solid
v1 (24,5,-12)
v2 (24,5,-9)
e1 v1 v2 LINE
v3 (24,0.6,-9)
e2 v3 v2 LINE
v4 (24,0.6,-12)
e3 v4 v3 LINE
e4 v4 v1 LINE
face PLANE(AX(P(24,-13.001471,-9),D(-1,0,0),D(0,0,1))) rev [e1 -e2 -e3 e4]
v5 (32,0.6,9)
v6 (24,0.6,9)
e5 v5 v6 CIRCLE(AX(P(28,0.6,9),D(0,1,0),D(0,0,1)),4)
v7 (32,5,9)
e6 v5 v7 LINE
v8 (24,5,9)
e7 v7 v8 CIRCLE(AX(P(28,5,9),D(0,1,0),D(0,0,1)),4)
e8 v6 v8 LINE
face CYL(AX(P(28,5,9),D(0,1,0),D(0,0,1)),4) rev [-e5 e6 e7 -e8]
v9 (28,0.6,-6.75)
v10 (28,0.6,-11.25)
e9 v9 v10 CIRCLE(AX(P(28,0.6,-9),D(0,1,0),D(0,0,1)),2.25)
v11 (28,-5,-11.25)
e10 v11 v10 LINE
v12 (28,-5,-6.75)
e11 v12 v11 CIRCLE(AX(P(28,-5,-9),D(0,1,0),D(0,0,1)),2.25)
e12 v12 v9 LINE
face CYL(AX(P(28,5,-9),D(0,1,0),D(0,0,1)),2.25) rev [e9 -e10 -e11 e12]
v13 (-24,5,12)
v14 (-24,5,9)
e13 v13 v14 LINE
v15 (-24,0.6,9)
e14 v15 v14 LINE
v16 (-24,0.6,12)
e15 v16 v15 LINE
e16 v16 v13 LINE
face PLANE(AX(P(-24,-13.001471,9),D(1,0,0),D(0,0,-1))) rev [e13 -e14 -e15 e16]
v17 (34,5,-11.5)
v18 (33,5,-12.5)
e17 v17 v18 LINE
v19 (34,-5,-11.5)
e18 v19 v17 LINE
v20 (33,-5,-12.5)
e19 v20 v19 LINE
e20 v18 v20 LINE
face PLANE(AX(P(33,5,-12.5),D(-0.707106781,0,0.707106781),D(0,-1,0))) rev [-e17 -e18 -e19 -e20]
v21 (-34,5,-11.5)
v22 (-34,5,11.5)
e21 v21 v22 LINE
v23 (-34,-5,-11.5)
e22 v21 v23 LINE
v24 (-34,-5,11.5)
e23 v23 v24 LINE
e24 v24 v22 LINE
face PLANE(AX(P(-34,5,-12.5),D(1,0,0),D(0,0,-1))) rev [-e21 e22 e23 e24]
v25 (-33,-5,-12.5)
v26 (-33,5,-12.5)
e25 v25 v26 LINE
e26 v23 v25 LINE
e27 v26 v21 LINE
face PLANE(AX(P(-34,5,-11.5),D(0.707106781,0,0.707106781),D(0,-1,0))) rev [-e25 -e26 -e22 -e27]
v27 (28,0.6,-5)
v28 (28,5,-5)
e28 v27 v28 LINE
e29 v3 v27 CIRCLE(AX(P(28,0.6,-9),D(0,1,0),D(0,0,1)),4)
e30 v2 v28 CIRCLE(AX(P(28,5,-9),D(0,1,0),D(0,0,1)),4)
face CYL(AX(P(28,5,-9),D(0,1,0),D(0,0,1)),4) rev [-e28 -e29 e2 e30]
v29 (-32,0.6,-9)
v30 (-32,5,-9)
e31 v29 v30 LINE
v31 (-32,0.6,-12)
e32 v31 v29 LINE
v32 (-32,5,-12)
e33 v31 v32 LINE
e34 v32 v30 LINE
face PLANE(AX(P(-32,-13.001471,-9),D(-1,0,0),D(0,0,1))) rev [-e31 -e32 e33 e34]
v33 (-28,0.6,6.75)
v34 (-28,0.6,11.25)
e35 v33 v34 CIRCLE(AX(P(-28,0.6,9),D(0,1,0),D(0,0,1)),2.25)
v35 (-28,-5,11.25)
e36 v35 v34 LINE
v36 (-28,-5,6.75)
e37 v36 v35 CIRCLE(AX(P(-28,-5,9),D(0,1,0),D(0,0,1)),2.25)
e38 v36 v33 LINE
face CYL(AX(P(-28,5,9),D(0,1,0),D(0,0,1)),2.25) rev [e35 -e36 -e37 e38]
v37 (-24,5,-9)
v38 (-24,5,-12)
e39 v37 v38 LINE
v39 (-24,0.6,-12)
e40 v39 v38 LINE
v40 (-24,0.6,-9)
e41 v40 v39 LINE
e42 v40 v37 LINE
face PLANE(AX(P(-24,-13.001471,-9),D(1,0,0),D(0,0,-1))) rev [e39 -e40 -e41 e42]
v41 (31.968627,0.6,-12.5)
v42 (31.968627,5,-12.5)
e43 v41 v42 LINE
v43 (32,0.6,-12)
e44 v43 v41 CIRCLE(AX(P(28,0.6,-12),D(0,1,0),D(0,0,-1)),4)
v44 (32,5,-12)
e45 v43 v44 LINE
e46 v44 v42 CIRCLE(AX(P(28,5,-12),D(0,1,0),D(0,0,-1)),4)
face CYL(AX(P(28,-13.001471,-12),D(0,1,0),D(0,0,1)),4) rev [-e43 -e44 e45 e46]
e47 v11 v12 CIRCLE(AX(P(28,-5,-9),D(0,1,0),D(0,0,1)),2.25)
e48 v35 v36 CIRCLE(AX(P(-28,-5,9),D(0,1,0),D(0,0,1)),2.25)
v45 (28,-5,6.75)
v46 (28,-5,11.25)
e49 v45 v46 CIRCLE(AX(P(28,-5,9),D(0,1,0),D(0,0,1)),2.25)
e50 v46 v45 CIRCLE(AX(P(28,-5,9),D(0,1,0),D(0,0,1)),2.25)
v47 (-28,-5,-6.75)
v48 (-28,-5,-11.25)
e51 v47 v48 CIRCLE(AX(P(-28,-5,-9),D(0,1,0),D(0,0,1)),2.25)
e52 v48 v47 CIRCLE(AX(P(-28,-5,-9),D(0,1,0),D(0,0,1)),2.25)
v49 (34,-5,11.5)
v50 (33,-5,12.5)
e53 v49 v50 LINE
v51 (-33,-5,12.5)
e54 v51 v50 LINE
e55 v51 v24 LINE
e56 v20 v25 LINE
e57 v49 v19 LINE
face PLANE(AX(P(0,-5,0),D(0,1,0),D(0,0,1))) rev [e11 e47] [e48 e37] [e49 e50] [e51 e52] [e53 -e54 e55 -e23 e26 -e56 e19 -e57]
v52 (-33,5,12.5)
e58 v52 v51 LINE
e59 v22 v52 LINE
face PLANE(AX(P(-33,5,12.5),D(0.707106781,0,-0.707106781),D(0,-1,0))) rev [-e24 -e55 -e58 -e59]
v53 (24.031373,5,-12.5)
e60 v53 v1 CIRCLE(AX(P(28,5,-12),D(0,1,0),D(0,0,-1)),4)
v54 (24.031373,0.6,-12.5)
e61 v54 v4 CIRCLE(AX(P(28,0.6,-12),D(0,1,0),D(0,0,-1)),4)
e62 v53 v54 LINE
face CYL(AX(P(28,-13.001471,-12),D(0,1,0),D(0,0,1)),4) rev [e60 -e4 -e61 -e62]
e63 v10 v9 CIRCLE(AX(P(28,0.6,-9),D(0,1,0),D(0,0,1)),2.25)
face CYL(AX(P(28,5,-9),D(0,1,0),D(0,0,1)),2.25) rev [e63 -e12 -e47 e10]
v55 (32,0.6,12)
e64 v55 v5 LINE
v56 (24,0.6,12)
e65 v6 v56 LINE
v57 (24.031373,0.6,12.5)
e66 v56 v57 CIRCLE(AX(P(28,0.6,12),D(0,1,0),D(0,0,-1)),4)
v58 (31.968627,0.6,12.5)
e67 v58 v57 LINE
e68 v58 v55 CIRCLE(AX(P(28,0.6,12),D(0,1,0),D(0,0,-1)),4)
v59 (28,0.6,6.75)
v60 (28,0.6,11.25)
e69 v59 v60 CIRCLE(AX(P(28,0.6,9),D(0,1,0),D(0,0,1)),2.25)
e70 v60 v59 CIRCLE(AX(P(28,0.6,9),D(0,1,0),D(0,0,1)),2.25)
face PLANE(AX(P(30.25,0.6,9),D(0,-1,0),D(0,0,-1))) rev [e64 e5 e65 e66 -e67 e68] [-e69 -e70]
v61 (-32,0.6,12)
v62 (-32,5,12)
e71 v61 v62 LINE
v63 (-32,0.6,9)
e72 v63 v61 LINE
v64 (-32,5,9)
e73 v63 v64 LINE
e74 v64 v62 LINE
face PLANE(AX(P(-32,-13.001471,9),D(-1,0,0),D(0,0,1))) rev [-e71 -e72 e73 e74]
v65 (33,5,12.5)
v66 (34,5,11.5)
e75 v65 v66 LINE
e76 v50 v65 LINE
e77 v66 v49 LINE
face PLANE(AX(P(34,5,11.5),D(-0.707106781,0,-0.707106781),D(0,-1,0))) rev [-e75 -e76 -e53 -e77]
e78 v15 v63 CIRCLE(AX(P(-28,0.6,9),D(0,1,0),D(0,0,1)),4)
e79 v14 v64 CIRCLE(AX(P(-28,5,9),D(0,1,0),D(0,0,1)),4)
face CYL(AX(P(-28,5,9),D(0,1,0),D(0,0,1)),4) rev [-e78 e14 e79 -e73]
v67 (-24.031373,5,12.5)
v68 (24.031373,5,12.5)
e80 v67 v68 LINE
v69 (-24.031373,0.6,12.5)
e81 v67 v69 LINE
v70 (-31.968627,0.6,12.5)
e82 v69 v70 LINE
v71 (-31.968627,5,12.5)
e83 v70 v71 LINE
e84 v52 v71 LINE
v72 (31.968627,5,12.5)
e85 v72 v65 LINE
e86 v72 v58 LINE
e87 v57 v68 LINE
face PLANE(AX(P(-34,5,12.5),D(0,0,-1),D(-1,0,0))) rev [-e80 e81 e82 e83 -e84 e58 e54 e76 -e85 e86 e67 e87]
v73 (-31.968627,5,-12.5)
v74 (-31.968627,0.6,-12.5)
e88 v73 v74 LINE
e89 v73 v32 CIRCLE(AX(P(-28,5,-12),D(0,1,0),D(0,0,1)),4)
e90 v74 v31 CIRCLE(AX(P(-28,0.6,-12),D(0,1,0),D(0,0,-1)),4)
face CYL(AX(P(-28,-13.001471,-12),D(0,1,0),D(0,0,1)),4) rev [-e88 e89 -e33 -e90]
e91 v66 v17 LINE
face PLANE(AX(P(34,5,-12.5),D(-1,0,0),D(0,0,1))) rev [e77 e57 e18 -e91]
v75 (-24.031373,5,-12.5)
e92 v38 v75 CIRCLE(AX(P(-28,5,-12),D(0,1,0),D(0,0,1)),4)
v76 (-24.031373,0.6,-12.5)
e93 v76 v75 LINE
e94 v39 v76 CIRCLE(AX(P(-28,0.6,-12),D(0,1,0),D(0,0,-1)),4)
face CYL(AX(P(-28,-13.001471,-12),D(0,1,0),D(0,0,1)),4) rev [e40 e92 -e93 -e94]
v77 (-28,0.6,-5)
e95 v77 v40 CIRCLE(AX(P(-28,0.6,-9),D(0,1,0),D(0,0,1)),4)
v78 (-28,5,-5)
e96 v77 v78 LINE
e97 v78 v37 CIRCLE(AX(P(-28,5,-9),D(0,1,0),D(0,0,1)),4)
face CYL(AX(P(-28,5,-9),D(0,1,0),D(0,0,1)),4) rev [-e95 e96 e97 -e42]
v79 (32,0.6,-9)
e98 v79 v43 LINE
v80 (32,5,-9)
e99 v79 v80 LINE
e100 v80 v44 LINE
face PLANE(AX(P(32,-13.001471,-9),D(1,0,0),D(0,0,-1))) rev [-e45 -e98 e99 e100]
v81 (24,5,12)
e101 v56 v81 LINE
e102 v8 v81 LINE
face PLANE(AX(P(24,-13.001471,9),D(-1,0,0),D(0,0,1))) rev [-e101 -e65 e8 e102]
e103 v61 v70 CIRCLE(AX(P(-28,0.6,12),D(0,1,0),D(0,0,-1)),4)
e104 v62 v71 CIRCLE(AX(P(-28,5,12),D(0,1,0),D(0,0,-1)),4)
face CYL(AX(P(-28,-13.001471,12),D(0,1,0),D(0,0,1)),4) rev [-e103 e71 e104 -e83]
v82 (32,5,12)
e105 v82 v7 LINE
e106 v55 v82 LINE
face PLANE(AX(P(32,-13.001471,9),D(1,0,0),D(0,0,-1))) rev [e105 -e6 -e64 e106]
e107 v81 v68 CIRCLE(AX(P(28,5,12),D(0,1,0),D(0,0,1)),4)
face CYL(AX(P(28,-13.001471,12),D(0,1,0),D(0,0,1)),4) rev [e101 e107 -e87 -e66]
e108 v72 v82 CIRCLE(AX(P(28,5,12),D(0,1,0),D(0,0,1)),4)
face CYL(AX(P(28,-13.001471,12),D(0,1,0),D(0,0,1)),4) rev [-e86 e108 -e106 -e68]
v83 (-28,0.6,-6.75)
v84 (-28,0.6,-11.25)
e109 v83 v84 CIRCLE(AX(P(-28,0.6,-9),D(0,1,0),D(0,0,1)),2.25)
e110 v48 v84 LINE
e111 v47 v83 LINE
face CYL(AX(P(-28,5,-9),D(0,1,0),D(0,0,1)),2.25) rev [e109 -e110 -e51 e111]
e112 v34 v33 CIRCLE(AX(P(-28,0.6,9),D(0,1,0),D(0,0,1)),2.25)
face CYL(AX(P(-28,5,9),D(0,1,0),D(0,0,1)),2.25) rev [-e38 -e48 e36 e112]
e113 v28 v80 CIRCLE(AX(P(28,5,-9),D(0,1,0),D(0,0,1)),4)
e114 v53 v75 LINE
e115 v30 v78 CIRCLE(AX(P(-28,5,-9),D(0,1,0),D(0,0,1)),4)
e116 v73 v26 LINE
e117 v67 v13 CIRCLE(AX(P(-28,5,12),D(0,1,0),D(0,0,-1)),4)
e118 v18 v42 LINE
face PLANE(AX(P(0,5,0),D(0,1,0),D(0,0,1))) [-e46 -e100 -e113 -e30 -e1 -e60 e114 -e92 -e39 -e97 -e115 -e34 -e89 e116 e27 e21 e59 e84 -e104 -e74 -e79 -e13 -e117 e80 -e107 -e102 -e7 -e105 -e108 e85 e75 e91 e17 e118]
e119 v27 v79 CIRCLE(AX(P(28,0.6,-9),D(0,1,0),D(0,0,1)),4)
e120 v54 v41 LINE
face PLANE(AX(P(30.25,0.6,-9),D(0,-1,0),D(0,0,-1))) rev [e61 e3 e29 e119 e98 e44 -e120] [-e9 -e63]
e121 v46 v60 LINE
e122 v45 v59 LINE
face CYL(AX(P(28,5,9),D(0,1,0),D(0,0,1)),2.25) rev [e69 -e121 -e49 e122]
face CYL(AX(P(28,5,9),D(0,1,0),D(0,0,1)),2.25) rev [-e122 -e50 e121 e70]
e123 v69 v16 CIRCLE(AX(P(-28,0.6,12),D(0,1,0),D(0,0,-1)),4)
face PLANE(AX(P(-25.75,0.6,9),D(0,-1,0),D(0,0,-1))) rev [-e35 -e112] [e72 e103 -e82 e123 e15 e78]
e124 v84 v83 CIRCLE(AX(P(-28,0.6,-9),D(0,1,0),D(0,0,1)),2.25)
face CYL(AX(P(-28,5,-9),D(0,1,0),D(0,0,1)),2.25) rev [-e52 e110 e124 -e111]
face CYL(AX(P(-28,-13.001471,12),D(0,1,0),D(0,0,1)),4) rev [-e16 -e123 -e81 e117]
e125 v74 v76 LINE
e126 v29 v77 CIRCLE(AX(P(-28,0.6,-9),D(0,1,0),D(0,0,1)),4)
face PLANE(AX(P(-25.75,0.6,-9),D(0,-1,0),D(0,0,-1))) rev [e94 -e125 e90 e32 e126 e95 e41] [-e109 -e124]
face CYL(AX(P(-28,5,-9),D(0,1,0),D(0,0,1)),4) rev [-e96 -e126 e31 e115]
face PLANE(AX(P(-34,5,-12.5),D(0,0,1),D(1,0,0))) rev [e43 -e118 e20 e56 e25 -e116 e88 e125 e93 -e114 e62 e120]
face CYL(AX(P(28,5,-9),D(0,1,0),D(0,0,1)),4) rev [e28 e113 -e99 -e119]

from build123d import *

# Parameters (mm, degrees)
SKETCH_1_W                   = 68
SKETCH_1_H                   = 25
EXTRUDE_1_DEPTH              = 5
HOLE_WIZARD_M4_1_D           = 4.5
HOLE_WIZARD_M4_1_CBORE_D     = 8
HOLE_WIZARD_M4_1_CBORE_DEPTH = 4.4
CUT_EXTRUDE_1_DEPTH          = 4.4
CHAMFER_1_SIZE               = 1


with BuildPart() as part:
    # 草图1 → 凸台-拉伸1 (new, symmetric)
    with BuildSketch(Plane(origin=(0, 0, 0), x_dir=(1, 0, 0), z_dir=(0, 1, 0))):
        Rectangle(SKETCH_1_W, SKETCH_1_H)
    extrude(amount=EXTRUDE_1_DEPTH, both=True)

    # M4 六角凹头螺钉的柱形沉头孔1 (through all)
    with Locations(Plane(origin=(0, 5, 0), x_dir=(1, 0, 0), z_dir=(0, 1, 0))):
        with Locations((-28, 9), (-28, -9), (28, 9), (28, -9)):
            CounterBoreHole(HOLE_WIZARD_M4_1_D / 2, HOLE_WIZARD_M4_1_CBORE_D / 2, HOLE_WIZARD_M4_1_CBORE_DEPTH)

    # 草图4 → 切除-拉伸1 (cut)
    with BuildSketch(Plane(origin=(0, 5, 0), x_dir=(1, 0, 0), z_dir=(0, 1, 0))):
        with BuildLine():
            Line((-32, 9), (-32, 12))
            ThreePointArc((-32, 12), (-28, 16), (-24, 12))
            Line((-24, 12), (-24, 9))
            ThreePointArc((-24, 9), (-28, 5), (-32, 9))
        make_face()
        with BuildLine():
            Line((-32, -9), (-32, -12))
            ThreePointArc((-32, -12), (-28, -16), (-24, -12))
            Line((-24, -12), (-24, -9))
            ThreePointArc((-24, -9), (-28, -5), (-32, -9))
        make_face()
        with BuildLine():
            Line((32, 9), (32, 12))
            ThreePointArc((32, 12), (28, 16), (24, 12))
            Line((24, 12), (24, 9))
            ThreePointArc((24, 9), (28, 5), (32, 9))
        make_face()
        with BuildLine():
            Line((32, -9), (32, -12))
            ThreePointArc((32, -12), (28, -16), (24, -12))
            Line((24, -12), (24, -9))
            ThreePointArc((24, -9), (28, -5), (32, -9))
        make_face()
    extrude(amount=-CUT_EXTRUDE_1_DEPTH, mode=Mode.SUBTRACT)

    # 倒角1
    chamfer_1_edges = [part.edges().sort_by_distance(p)[0] for p in [
        (34, 0, 12.5),
        (-34, 0, 12.5),
        (-34, 0, -12.5),
        (34, 0, -12.5),
    ]]
    chamfer(chamfer_1_edges, length=CHAMFER_1_SIZE)


solid = part.part
